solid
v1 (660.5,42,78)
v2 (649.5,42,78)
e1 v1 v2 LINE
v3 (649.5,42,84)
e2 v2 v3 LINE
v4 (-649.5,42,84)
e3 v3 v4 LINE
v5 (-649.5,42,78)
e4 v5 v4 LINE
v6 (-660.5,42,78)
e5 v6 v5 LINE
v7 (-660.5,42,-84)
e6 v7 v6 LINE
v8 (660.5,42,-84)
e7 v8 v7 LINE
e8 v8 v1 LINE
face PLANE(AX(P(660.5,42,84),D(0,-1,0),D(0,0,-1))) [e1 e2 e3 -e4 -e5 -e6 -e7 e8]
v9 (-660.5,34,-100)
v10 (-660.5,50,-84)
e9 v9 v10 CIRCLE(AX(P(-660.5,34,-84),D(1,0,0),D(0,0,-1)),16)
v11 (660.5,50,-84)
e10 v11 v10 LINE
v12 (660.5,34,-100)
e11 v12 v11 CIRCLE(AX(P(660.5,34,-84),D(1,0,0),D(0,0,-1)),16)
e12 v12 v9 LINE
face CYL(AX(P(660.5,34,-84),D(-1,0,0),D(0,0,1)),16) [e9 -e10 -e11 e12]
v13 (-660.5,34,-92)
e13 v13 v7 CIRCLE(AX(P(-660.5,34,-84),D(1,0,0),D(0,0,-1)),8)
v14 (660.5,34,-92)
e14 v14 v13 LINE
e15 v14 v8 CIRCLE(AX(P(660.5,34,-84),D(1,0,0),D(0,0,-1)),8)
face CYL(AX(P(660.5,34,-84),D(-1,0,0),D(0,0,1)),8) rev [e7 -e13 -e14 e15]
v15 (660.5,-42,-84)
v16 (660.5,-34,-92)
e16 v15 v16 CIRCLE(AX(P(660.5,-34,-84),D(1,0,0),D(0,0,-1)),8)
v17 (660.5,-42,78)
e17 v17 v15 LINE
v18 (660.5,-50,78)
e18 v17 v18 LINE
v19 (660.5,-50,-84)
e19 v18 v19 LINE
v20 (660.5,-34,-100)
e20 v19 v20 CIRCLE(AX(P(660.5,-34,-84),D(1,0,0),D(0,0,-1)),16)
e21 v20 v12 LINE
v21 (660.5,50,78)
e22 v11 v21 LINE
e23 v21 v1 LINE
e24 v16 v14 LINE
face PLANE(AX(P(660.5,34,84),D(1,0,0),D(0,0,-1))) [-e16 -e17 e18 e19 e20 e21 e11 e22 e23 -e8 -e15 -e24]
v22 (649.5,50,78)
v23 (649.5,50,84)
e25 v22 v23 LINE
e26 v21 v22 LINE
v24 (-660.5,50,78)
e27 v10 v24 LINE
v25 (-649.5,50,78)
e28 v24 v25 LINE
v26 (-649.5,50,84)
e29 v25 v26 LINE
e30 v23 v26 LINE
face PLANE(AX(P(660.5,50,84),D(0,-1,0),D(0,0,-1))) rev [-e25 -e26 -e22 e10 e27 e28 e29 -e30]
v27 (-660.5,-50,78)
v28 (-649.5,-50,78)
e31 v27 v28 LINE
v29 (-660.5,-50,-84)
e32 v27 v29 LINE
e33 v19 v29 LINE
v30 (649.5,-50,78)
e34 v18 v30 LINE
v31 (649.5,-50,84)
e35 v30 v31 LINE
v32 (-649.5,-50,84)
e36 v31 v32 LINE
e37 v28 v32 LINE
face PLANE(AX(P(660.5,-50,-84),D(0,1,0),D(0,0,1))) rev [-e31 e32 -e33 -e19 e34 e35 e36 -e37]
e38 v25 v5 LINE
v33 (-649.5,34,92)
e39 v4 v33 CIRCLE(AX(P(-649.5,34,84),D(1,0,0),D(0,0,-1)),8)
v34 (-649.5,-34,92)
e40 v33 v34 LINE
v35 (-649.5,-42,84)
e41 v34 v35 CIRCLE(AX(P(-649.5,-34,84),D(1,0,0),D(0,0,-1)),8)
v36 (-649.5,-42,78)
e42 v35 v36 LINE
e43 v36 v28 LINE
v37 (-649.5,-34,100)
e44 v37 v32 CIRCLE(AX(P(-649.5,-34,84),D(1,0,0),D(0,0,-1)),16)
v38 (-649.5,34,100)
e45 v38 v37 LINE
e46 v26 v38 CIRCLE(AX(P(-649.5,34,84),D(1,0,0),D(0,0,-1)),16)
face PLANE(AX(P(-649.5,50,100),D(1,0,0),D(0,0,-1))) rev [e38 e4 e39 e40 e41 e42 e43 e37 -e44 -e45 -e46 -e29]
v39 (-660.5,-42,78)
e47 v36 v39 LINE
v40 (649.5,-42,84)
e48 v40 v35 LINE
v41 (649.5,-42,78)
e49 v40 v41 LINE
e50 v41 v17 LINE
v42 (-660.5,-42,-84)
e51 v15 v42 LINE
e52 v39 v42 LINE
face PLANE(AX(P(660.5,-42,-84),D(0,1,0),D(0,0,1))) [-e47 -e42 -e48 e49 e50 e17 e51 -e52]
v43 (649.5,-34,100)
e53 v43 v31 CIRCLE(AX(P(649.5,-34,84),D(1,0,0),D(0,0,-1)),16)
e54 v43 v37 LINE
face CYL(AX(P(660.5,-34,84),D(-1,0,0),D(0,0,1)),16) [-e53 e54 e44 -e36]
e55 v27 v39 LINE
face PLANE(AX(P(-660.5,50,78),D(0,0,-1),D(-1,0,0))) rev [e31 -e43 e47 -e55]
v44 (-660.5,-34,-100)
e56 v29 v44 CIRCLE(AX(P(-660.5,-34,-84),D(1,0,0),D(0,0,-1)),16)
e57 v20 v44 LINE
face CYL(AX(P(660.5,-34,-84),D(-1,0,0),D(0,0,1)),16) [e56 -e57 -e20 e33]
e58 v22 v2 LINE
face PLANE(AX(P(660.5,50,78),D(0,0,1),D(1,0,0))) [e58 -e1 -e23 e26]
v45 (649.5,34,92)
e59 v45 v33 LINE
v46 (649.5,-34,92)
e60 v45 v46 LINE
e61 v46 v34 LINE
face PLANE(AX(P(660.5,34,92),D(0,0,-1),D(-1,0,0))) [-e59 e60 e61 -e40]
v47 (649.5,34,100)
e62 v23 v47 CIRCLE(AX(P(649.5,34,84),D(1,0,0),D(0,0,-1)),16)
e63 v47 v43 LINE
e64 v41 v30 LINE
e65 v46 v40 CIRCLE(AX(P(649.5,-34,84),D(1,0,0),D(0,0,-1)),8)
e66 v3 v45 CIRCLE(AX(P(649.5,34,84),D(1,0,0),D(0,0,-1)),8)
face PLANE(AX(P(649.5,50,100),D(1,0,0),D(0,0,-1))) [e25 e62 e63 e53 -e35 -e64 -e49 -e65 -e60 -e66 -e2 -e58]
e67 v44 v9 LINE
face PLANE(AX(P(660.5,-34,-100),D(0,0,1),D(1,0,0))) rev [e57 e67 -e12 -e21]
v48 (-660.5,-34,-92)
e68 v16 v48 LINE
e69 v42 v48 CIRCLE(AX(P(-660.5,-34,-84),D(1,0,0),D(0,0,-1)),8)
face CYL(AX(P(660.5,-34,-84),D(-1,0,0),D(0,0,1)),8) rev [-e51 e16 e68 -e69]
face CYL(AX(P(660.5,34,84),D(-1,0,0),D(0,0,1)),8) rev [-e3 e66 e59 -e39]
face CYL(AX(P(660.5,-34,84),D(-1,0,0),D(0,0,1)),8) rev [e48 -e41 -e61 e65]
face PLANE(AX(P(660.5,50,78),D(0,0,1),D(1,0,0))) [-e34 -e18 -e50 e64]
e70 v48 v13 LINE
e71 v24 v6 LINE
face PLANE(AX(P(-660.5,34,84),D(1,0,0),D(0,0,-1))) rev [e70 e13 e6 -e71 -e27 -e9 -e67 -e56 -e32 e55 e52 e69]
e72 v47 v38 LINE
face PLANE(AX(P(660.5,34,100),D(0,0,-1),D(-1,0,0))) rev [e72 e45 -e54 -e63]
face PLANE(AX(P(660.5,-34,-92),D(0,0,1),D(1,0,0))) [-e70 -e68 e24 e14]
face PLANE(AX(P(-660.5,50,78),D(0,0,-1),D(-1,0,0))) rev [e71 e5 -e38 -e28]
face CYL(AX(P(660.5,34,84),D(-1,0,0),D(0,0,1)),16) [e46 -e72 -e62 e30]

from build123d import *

# Parameters (mm, degrees)
STRUCTURAL_COLD_FORMED_RECTANGULAR_HOLLO_DEPTH = 1321
SKETCH2_W                                      = 11
SKETCH2_H                                      = 22
CUT_EXTRUDE1_DEPTH                             = 676.470391653


with BuildPart() as part:
    # Sketch1 → Structural cold-formed rectangular hollow section (gb t6728-2002) 200×100×8(1) (new body)
    with BuildSketch(Plane.YZ.offset(-660.5)):
        with BuildLine():
            Line((-34, -100), (34, -100))
            ThreePointArc((34, -100), (45.313708499, -95.313708499), (50, -84))
            Line((50, -84), (50, 84))
            ThreePointArc((50, 84), (45.313708499, 95.313708499), (34, 100))
            Line((34, 100), (-34, 100))
            ThreePointArc((-34, 100), (-45.313708499, 95.313708499), (-50, 84))
            Line((-50, 84), (-50, -84))
            ThreePointArc((-50, -84), (-45.313708499, -95.313708499), (-34, -100))
        make_face()
        with BuildLine():
            Line((-34, -92), (34, -92))
            ThreePointArc((34, -92), (39.656854249, -89.656854249), (42, -84))
            Line((42, -84), (42, 84))
            ThreePointArc((42, 84), (39.656854249, 89.656854249), (34, 92))
            Line((34, 92), (-34, 92))
            ThreePointArc((-34, 92), (-39.656854249, 89.656854249), (-42, 84))
            Line((-42, 84), (-42, -84))
            ThreePointArc((-42, -84), (-39.656854249, -89.656854249), (-34, -92))
        make_face(mode=Mode.SUBTRACT)
    extrude(amount=STRUCTURAL_COLD_FORMED_RECTANGULAR_HOLLO_DEPTH)

    # Sketch2 → Cut-Extrude1 (cut, through all)
    with BuildSketch(Plane.XZ.offset(50)):
        with Locations((-655, 89)):
            Rectangle(SKETCH2_W, SKETCH2_H)
    cut_extrude1 = extrude(amount=-CUT_EXTRUDE1_DEPTH, mode=Mode.SUBTRACT)

    # Mirror1: Cut-Extrude1 across plane
    add(cut_extrude1.mirror(Plane(origin=(0, 0, 0), x_dir=(0, 0, 1), z_dir=(1, 0, 0))), mode=Mode.SUBTRACT)


solid = part.part
